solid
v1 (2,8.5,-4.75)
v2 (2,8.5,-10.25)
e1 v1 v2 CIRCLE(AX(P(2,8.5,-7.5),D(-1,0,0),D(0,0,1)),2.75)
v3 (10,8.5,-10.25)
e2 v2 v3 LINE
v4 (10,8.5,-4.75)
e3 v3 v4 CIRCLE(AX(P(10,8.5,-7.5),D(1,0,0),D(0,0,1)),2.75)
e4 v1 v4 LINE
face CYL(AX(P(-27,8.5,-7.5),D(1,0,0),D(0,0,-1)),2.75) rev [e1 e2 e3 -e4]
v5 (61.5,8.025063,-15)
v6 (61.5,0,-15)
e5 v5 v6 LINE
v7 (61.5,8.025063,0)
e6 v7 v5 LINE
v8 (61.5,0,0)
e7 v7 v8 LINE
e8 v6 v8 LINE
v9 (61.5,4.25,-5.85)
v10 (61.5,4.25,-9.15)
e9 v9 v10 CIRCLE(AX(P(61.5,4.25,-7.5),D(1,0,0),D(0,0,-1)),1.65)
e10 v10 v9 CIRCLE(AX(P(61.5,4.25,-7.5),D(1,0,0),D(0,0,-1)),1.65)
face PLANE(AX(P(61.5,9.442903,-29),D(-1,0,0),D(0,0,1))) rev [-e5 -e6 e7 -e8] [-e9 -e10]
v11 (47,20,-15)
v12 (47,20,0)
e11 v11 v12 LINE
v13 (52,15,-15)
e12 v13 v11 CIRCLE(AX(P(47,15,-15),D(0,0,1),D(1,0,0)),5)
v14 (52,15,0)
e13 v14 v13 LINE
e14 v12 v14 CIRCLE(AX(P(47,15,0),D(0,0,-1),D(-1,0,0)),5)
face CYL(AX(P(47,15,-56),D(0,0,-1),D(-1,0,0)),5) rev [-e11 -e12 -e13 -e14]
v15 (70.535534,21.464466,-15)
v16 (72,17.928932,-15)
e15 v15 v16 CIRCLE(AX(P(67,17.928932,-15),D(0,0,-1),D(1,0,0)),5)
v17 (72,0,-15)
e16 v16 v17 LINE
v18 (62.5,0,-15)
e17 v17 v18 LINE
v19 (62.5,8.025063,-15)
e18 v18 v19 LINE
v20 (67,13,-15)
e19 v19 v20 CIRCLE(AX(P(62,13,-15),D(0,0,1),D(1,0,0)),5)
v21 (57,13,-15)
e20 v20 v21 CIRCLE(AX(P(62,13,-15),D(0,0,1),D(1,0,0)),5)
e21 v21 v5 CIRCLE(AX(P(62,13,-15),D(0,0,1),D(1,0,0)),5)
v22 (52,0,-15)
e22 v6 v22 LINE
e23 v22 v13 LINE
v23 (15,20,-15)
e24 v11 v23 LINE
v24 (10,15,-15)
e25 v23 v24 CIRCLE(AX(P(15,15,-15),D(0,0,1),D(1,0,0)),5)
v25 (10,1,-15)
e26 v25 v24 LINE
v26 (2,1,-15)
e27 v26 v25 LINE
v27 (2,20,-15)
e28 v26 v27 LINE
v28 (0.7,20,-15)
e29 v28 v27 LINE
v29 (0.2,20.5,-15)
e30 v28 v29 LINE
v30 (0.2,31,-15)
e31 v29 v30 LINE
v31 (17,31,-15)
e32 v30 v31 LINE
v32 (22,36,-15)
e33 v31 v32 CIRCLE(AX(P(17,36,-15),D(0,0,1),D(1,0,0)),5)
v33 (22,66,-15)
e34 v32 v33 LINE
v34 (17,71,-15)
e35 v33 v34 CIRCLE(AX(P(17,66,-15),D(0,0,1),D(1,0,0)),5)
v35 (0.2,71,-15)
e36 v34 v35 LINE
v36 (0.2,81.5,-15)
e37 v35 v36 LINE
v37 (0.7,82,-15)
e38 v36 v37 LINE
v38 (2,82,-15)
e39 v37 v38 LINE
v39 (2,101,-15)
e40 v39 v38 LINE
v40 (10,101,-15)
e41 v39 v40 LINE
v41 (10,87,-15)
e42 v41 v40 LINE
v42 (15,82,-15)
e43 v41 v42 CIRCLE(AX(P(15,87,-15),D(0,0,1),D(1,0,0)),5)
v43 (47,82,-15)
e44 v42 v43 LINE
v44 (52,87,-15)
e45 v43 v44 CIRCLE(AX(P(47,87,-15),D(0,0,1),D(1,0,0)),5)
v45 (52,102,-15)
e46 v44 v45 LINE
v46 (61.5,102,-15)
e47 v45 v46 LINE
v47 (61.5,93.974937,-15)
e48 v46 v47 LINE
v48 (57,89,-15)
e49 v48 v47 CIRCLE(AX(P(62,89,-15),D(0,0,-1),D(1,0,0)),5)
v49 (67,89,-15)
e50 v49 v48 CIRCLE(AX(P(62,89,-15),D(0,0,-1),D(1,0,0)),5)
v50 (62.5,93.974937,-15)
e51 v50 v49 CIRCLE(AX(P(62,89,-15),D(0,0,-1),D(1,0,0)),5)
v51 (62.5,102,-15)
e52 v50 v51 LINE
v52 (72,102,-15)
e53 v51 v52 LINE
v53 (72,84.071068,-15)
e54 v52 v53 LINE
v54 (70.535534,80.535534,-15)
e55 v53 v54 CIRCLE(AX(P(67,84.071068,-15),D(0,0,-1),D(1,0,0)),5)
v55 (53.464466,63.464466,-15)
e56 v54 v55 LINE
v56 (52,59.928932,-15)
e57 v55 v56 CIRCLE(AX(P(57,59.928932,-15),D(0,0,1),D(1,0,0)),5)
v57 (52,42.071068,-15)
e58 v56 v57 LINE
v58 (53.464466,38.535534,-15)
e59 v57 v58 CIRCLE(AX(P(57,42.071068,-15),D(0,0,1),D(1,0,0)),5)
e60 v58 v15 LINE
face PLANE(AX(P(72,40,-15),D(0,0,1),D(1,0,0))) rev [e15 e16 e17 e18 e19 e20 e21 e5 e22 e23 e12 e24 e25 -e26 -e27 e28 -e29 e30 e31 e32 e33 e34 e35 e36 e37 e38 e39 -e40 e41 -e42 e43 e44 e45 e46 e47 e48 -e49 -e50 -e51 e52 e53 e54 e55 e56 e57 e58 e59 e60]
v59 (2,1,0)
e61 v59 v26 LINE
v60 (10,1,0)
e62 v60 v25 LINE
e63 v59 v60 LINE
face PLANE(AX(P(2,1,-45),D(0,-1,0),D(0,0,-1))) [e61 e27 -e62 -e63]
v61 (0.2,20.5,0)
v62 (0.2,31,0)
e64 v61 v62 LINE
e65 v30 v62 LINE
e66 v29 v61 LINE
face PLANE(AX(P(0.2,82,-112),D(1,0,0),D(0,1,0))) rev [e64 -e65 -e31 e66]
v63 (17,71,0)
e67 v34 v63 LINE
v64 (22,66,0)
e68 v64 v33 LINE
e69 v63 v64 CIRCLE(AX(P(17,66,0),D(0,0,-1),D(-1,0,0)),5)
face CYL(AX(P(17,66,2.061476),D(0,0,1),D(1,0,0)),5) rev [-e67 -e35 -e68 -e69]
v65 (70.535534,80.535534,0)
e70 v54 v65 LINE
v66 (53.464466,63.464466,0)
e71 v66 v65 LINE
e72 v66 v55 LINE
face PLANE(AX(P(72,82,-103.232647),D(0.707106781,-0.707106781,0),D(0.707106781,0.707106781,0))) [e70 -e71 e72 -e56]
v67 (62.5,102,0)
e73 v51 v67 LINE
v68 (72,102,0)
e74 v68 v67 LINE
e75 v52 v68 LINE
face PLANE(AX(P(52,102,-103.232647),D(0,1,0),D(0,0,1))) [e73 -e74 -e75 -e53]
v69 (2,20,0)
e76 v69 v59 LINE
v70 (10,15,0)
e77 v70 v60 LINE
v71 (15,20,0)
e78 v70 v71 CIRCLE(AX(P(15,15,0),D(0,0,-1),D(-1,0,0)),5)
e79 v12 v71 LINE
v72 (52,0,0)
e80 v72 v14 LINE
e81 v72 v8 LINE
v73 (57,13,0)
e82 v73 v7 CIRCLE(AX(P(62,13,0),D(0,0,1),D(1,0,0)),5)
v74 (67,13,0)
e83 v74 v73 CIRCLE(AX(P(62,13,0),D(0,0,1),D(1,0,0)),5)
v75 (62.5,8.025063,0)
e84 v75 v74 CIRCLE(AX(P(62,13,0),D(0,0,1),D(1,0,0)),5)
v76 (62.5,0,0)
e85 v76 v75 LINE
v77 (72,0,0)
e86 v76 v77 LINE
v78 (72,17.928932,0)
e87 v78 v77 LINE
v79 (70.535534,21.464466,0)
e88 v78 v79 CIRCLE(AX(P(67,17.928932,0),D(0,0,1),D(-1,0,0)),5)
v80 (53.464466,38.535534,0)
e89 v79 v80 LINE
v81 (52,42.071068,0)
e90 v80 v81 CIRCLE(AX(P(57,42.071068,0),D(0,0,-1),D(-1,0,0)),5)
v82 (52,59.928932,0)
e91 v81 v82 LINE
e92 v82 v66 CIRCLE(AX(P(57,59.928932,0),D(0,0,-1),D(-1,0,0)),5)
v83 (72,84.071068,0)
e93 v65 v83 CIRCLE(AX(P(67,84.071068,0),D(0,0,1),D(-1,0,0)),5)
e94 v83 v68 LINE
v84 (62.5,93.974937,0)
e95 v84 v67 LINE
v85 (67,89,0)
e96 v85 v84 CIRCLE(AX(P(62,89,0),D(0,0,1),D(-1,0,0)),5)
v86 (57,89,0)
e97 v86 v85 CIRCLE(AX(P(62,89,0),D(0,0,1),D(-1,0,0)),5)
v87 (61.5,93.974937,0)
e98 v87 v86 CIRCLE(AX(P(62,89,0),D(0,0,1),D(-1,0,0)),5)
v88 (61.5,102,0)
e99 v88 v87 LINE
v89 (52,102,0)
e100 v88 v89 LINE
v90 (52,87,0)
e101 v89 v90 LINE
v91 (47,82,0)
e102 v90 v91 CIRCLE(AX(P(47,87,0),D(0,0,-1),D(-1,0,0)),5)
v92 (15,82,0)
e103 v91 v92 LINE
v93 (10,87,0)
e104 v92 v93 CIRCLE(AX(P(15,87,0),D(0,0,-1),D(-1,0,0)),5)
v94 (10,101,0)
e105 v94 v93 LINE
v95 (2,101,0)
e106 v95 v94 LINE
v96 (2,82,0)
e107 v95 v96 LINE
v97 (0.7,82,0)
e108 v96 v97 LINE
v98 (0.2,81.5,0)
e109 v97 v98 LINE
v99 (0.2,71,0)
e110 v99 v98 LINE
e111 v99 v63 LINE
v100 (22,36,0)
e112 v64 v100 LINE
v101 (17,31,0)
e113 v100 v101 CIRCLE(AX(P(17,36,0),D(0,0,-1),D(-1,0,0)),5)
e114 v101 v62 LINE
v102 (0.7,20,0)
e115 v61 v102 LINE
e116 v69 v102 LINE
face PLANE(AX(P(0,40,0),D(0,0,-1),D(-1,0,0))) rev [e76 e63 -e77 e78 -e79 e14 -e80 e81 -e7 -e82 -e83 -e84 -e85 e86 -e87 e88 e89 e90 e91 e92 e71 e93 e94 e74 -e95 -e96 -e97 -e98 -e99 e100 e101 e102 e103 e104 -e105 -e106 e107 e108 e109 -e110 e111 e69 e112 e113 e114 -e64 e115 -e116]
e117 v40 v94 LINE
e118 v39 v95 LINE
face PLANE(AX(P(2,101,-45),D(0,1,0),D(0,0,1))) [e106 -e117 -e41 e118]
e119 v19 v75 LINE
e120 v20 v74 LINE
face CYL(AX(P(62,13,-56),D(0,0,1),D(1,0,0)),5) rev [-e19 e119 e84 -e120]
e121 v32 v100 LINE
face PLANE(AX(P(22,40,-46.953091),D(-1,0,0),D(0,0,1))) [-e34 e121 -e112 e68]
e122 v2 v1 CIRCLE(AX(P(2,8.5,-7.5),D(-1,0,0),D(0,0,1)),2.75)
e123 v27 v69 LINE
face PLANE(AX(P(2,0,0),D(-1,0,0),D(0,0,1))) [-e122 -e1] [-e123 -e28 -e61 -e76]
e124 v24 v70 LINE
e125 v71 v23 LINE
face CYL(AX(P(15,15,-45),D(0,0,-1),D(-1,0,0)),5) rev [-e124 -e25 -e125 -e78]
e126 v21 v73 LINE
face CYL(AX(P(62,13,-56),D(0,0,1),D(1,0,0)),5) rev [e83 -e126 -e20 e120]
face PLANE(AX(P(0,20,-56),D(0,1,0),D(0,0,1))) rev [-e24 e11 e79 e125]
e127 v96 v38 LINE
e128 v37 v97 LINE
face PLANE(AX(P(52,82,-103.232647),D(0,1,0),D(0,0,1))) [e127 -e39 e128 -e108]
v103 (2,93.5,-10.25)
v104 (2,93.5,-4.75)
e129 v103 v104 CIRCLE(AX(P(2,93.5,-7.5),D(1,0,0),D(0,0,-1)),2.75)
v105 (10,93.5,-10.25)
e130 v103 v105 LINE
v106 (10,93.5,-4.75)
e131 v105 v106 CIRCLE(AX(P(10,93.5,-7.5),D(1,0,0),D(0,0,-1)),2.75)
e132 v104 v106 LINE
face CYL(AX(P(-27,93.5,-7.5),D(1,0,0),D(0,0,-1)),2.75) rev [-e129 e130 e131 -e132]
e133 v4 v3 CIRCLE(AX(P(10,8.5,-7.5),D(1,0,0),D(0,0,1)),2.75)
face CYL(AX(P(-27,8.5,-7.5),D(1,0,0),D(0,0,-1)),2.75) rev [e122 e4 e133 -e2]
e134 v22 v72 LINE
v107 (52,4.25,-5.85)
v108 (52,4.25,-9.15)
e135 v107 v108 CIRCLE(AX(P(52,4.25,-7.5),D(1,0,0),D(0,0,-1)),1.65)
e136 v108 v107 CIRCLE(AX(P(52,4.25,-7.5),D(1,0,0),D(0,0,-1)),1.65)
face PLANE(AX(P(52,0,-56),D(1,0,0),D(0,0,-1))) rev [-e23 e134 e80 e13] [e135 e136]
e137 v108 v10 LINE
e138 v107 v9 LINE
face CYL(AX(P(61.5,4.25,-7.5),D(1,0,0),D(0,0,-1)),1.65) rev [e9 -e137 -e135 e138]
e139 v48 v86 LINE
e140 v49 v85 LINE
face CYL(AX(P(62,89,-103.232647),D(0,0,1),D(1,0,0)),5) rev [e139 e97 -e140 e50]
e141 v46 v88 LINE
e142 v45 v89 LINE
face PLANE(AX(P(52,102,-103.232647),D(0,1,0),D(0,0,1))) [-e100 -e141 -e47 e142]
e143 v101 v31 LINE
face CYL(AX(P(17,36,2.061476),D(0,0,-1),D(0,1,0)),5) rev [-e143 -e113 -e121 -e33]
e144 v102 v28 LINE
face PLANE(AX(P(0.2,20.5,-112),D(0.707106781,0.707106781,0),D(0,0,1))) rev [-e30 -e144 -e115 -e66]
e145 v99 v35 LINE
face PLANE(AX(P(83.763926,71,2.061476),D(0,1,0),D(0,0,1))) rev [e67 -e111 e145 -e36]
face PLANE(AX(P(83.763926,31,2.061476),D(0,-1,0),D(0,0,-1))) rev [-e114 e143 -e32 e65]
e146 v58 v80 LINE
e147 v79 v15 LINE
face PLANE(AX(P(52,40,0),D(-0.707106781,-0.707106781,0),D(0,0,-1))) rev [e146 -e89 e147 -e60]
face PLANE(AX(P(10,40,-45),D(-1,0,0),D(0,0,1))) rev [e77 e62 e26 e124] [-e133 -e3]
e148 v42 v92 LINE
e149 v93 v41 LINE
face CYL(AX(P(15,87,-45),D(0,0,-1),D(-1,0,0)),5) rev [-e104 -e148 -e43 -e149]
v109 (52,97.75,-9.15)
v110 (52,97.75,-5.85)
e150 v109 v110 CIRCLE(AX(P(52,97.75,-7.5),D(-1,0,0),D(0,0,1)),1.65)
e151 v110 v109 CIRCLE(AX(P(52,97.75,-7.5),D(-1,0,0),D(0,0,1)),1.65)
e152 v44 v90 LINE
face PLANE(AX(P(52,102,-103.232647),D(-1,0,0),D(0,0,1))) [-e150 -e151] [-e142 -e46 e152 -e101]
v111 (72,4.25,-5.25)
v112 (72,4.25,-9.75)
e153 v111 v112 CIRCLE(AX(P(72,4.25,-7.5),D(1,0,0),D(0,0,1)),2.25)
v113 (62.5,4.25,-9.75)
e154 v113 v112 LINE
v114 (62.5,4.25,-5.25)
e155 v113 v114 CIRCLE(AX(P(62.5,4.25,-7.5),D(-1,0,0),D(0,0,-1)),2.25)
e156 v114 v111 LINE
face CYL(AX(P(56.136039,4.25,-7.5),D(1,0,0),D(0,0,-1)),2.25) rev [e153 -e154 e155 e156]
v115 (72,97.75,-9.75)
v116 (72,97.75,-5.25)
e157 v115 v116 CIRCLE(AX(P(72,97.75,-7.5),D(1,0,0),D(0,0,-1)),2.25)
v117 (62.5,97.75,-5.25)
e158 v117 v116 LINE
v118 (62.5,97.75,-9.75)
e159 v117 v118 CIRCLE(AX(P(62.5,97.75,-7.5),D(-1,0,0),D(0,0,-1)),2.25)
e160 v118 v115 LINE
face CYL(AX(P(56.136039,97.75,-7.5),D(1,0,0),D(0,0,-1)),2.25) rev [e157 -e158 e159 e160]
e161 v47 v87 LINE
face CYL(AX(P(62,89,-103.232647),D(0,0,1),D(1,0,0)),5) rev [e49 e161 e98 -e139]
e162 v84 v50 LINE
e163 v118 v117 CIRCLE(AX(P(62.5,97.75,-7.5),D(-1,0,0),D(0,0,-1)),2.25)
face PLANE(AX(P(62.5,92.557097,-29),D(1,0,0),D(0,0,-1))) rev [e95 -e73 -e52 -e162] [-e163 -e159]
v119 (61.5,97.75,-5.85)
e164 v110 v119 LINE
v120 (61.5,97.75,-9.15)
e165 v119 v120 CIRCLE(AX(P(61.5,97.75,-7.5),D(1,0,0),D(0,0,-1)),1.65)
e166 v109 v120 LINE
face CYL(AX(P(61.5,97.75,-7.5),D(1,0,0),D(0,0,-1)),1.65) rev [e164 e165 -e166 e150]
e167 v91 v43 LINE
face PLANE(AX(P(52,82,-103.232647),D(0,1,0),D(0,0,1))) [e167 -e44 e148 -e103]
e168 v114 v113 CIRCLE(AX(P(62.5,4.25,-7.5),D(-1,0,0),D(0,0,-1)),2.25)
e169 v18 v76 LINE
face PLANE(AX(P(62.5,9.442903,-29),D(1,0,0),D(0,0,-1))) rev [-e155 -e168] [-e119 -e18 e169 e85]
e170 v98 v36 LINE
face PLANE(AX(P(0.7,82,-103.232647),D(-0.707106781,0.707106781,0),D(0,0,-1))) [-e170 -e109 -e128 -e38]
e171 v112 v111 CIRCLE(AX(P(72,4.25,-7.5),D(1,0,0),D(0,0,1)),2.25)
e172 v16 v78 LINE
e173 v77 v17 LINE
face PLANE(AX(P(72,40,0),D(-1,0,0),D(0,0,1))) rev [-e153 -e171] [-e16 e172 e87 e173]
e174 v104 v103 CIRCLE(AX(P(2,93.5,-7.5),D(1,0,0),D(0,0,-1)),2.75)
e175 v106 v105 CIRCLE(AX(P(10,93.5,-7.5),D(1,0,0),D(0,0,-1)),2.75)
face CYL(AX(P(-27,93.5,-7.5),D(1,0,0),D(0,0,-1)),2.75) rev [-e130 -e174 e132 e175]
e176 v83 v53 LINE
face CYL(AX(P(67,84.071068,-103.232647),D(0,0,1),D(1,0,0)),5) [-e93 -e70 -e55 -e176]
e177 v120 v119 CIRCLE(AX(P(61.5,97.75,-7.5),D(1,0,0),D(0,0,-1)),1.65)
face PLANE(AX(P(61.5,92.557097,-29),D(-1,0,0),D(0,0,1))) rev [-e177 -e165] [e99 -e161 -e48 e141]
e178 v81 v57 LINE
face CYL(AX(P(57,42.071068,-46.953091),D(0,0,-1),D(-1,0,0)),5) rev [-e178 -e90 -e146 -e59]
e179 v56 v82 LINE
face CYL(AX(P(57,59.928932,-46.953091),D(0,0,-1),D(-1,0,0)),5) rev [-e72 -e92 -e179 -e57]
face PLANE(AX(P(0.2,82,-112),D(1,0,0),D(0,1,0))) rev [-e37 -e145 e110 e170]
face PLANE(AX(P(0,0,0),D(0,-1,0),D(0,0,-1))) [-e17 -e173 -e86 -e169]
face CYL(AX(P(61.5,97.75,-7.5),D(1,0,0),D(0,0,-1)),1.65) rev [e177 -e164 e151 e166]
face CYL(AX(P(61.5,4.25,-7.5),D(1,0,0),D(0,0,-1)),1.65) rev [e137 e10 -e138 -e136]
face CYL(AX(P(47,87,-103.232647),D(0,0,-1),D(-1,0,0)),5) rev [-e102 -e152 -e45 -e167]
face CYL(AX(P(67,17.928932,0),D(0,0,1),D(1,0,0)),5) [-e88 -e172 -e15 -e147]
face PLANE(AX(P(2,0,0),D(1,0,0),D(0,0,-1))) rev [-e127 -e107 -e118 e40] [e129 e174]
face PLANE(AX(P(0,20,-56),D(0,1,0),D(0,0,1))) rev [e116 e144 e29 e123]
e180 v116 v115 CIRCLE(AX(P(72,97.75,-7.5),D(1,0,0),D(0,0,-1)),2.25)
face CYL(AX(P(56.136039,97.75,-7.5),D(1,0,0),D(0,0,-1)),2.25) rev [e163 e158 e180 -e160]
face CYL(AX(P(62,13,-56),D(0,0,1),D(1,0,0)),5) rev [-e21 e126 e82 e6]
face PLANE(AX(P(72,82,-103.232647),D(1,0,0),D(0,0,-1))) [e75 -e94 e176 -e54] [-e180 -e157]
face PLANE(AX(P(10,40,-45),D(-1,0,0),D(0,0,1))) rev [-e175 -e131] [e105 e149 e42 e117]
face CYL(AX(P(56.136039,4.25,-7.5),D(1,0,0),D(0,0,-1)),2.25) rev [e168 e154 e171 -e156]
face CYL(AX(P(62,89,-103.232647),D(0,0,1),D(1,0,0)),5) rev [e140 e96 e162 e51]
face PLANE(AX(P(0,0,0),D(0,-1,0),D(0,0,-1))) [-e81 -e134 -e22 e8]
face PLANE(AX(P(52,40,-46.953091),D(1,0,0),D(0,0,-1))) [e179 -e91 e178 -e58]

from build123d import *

# Parameters (mm, degrees)
BOSS_EXTRUDE1_DEPTH   = 40
SKETCH2_W             = 52
SKETCH2_H             = 20
CUT_EXTRUDE1_DEPTH    = 56
SKETCH3_R             = 5
CUT_EXTRUDE2_DEPTH    = 56
CHAMFER1_SIZE         = 20
SKETCH4_W             = 30
SKETCH4_H             = 11
BOSS_EXTRUDE2_DEPTH   = 15
SKETCH5_R             = 5
BOSS_EXTRUDE3_DEPTH   = 15
SKETCH6_W             = 45
SKETCH6_H             = 20
BOSS_EXTRUDE4_DEPTH   = 10
CUT_EXTRUDE3_REACH    = 134.714
SKETCH8_W             = 47.061475946
SKETCH8_H             = 40
SKETCH9_W             = 45
SKETCH9_H             = 19
BOSS_EXTRUDE5_DEPTH   = 8
SKETCH11_R            = 2.75
CUT_EXTRUDE4_DEPTH    = 37
SKETCH12_W            = 30
SKETCH12_H            = 100
CUT_EXTRUDE5_DEPTH    = 112
SKETCH13_W            = 0.2
SKETCH13_H            = 62
CUT_EXTRUDE6_DEPTH    = 112
CHAMFER2_SIZE         = 0.5
SKETCH14_W            = 1
SKETCH14_H            = 9.442903458
CUT_EXTRUDE7_DEPTH    = 29
SKETCH15_R            = 2.25
CUT_EXTRUDE8_DEPTH    = 9.5
M4_TAPPED_HOLE1_D     = 3.3
M4_TAPPED_HOLE1_DEPTH = 9.5
M4_TAPPED_HOLE2_D     = 3.3
M4_TAPPED_HOLE2_DEPTH = 9.5
FILLET1_R             = 5


with BuildPart() as part:
    # Sketch1 → Boss-Extrude1 (new body)
    with BuildSketch(Plane(origin=(0, 0, 0), x_dir=(1, 0, 0), z_dir=(0, 1, 0))):
        Polygon((0, 0), (72, 0), (72, 15), (10, 15), (10, 45), (0, 45), align=None)
    extrude(amount=BOSS_EXTRUDE1_DEPTH)

    # Sketch2 → Cut-Extrude1 (cut)
    with BuildSketch(Plane.XY):
        with Locations((26, 10)):
            Rectangle(SKETCH2_W, SKETCH2_H)
    extrude(amount=-CUT_EXTRUDE1_DEPTH, mode=Mode.SUBTRACT)

    # Sketch3 → Cut-Extrude2 (cut)
    with BuildSketch(Plane.XY):
        with Locations((62, 13)):
            Circle(SKETCH3_R)
    extrude(amount=-CUT_EXTRUDE2_DEPTH, mode=Mode.SUBTRACT)

    # Chamfer1
    chamfer1_edges = [part.edges().sort_by_distance(p)[0] for p in [
        (72, 40, -7.5),
    ]]
    chamfer(chamfer1_edges, length=CHAMFER1_SIZE)

    # Sketch4 → Boss-Extrude2 (add)
    with BuildSketch(Plane.XY):
        with Locations((37, 45.5)):
            Rectangle(SKETCH4_W, SKETCH4_H)
    extrude(amount=-BOSS_EXTRUDE2_DEPTH)

    # Sketch5 → Boss-Extrude3 (add)
    with BuildSketch(Plane.XY):
        Polygon((22, 51), (52, 51), (52, 62), (72, 82), (72, 102), (52, 102), (52, 82), (0, 82), (0, 62), (22, 62), align=None)
        with Locations((62, 89)):
            Circle(SKETCH5_R, mode=Mode.SUBTRACT)
    extrude(amount=-BOSS_EXTRUDE3_DEPTH)

    # Sketch6 → Boss-Extrude4 (add)
    with BuildSketch(Plane.ZY):
        with Locations((-22.5, 30)):
            Rectangle(SKETCH6_W, SKETCH6_H)
        with Locations((-22.5, 72)):
            Rectangle(SKETCH6_W, SKETCH6_H)
    extrude(amount=-BOSS_EXTRUDE4_DEPTH)

    # Cut-Extrude3: up to this face of the body (flat: up to its plane)
    cut_extrude3_end = Plane(part.part.faces().sort_by_distance((22, 51, -7.5))[0])
    # Sketch8 → Cut-Extrude3 (cut, up to the picked face)
    with BuildSketch(Plane.ZY, mode=Mode.PRIVATE) as cut_extrude3_sk1:
        with Locations((-21.469262027, 51)):
            Rectangle(SKETCH8_W, SKETCH8_H)
    cut_extrude3_tool1 = split(extrude(cut_extrude3_sk1.sketch, amount=-CUT_EXTRUDE3_REACH, mode=Mode.PRIVATE), bisect_by=cut_extrude3_end, keep=Keep.BOTH, mode=Mode.PRIVATE)
    add(cut_extrude3_tool1.solids().sort_by(Axis((0, 51, -21.469262), (1, 0, 0)))[0], mode=Mode.SUBTRACT)

    # Sketch9 → Boss-Extrude5 (add)
    with BuildSketch(Plane(origin=(10, 0, 0), x_dir=(0, 0, -1), z_dir=(1, 0, 0))):
        with Locations((22.5, 91.5)):
            Rectangle(SKETCH9_W, SKETCH9_H)
        with Locations((22.5, 10.5)):
            Rectangle(SKETCH9_W, SKETCH9_H)
    extrude(amount=-BOSS_EXTRUDE5_DEPTH)

    # Sketch11 → Cut-Extrude4 (cut)
    with BuildSketch(Plane(origin=(10, 0, 0), x_dir=(0, 0, -1), z_dir=(1, 0, 0))):
        with Locations((7.5, 93.5)):
            Circle(SKETCH11_R)
        with Locations(Location((7.5, 8.5, 0), (0, 0, 180))):
            Circle(SKETCH11_R)
    extrude(amount=-CUT_EXTRUDE4_DEPTH, mode=Mode.SUBTRACT)

    # Sketch12 → Cut-Extrude5 (cut)
    with BuildSketch(Plane(origin=(72, 0, 0), x_dir=(0, 0, -1), z_dir=(1, 0, 0))):
        with Locations((30, 51)):
            Rectangle(SKETCH12_W, SKETCH12_H)
    extrude(amount=-CUT_EXTRUDE5_DEPTH, mode=Mode.SUBTRACT)

    # Sketch13 → Cut-Extrude6 (cut)
    with BuildSketch(Plane.XY):
        with Locations((0.1, 51)):
            Rectangle(SKETCH13_W, SKETCH13_H)
    extrude(amount=-CUT_EXTRUDE6_DEPTH, mode=Mode.SUBTRACT)

    # Chamfer2
    chamfer2_edges = [part.edges().sort_by_distance(p)[0] for p in [
        (0.2, 20, -7.5),
        (0.2, 82, -7.5),
    ]]
    chamfer(chamfer2_edges, length=CHAMFER2_SIZE)

    # Sketch14 → Cut-Extrude7 (cut)
    with BuildSketch(Plane.XY):
        with Locations((62, 4.721451729)):
            Rectangle(SKETCH14_W, SKETCH14_H)
        with Locations((62, 97.278548271)):
            Rectangle(SKETCH14_W, SKETCH14_H)
    extrude(amount=-CUT_EXTRUDE7_DEPTH, mode=Mode.SUBTRACT)

    # Sketch15 → Cut-Extrude8 (cut)
    with BuildSketch(Plane(origin=(72, 0, 0), x_dir=(0, 0, -1), z_dir=(1, 0, 0))):
        with Locations((7.5, 97.75)):
            Circle(SKETCH15_R)
        with Locations((7.5, 4.25)):
            Circle(SKETCH15_R)
    extrude(amount=-CUT_EXTRUDE8_DEPTH, mode=Mode.SUBTRACT)

    # M4 Tapped Hole1
    with Locations(Plane(origin=(61.5, 97.75, -7.5), x_dir=(0, 0, 1), z_dir=(1, 0, 0))):
        with Locations((0, 0)):
            Hole(M4_TAPPED_HOLE1_D / 2, depth=M4_TAPPED_HOLE1_DEPTH)

    # M4 Tapped Hole2
    with Locations(Plane(origin=(61.5, 4.25, -7.5), x_dir=(0, 0, 1), z_dir=(1, 0, 0))):
        with Locations((0, 0)):
            Hole(M4_TAPPED_HOLE2_D / 2, depth=M4_TAPPED_HOLE2_DEPTH)

    # Fillet1
    fillet1_edges = [part.edges().sort_by_distance(p)[0] for p in [
        (72, 20, -7.5),
        (72, 82, -7.5),
        (52, 62, -7.5),
        (52, 40, -7.5),
        (52, 82, -7.5),
        (10, 82, -7.5),
        (22, 71, -7.5),
        (22, 31, -7.5),
        (10, 20, -7.5),
        (52, 20, -7.5),
    ]]
    fillet(fillet1_edges, radius=FILLET1_R)


solid = part.part
